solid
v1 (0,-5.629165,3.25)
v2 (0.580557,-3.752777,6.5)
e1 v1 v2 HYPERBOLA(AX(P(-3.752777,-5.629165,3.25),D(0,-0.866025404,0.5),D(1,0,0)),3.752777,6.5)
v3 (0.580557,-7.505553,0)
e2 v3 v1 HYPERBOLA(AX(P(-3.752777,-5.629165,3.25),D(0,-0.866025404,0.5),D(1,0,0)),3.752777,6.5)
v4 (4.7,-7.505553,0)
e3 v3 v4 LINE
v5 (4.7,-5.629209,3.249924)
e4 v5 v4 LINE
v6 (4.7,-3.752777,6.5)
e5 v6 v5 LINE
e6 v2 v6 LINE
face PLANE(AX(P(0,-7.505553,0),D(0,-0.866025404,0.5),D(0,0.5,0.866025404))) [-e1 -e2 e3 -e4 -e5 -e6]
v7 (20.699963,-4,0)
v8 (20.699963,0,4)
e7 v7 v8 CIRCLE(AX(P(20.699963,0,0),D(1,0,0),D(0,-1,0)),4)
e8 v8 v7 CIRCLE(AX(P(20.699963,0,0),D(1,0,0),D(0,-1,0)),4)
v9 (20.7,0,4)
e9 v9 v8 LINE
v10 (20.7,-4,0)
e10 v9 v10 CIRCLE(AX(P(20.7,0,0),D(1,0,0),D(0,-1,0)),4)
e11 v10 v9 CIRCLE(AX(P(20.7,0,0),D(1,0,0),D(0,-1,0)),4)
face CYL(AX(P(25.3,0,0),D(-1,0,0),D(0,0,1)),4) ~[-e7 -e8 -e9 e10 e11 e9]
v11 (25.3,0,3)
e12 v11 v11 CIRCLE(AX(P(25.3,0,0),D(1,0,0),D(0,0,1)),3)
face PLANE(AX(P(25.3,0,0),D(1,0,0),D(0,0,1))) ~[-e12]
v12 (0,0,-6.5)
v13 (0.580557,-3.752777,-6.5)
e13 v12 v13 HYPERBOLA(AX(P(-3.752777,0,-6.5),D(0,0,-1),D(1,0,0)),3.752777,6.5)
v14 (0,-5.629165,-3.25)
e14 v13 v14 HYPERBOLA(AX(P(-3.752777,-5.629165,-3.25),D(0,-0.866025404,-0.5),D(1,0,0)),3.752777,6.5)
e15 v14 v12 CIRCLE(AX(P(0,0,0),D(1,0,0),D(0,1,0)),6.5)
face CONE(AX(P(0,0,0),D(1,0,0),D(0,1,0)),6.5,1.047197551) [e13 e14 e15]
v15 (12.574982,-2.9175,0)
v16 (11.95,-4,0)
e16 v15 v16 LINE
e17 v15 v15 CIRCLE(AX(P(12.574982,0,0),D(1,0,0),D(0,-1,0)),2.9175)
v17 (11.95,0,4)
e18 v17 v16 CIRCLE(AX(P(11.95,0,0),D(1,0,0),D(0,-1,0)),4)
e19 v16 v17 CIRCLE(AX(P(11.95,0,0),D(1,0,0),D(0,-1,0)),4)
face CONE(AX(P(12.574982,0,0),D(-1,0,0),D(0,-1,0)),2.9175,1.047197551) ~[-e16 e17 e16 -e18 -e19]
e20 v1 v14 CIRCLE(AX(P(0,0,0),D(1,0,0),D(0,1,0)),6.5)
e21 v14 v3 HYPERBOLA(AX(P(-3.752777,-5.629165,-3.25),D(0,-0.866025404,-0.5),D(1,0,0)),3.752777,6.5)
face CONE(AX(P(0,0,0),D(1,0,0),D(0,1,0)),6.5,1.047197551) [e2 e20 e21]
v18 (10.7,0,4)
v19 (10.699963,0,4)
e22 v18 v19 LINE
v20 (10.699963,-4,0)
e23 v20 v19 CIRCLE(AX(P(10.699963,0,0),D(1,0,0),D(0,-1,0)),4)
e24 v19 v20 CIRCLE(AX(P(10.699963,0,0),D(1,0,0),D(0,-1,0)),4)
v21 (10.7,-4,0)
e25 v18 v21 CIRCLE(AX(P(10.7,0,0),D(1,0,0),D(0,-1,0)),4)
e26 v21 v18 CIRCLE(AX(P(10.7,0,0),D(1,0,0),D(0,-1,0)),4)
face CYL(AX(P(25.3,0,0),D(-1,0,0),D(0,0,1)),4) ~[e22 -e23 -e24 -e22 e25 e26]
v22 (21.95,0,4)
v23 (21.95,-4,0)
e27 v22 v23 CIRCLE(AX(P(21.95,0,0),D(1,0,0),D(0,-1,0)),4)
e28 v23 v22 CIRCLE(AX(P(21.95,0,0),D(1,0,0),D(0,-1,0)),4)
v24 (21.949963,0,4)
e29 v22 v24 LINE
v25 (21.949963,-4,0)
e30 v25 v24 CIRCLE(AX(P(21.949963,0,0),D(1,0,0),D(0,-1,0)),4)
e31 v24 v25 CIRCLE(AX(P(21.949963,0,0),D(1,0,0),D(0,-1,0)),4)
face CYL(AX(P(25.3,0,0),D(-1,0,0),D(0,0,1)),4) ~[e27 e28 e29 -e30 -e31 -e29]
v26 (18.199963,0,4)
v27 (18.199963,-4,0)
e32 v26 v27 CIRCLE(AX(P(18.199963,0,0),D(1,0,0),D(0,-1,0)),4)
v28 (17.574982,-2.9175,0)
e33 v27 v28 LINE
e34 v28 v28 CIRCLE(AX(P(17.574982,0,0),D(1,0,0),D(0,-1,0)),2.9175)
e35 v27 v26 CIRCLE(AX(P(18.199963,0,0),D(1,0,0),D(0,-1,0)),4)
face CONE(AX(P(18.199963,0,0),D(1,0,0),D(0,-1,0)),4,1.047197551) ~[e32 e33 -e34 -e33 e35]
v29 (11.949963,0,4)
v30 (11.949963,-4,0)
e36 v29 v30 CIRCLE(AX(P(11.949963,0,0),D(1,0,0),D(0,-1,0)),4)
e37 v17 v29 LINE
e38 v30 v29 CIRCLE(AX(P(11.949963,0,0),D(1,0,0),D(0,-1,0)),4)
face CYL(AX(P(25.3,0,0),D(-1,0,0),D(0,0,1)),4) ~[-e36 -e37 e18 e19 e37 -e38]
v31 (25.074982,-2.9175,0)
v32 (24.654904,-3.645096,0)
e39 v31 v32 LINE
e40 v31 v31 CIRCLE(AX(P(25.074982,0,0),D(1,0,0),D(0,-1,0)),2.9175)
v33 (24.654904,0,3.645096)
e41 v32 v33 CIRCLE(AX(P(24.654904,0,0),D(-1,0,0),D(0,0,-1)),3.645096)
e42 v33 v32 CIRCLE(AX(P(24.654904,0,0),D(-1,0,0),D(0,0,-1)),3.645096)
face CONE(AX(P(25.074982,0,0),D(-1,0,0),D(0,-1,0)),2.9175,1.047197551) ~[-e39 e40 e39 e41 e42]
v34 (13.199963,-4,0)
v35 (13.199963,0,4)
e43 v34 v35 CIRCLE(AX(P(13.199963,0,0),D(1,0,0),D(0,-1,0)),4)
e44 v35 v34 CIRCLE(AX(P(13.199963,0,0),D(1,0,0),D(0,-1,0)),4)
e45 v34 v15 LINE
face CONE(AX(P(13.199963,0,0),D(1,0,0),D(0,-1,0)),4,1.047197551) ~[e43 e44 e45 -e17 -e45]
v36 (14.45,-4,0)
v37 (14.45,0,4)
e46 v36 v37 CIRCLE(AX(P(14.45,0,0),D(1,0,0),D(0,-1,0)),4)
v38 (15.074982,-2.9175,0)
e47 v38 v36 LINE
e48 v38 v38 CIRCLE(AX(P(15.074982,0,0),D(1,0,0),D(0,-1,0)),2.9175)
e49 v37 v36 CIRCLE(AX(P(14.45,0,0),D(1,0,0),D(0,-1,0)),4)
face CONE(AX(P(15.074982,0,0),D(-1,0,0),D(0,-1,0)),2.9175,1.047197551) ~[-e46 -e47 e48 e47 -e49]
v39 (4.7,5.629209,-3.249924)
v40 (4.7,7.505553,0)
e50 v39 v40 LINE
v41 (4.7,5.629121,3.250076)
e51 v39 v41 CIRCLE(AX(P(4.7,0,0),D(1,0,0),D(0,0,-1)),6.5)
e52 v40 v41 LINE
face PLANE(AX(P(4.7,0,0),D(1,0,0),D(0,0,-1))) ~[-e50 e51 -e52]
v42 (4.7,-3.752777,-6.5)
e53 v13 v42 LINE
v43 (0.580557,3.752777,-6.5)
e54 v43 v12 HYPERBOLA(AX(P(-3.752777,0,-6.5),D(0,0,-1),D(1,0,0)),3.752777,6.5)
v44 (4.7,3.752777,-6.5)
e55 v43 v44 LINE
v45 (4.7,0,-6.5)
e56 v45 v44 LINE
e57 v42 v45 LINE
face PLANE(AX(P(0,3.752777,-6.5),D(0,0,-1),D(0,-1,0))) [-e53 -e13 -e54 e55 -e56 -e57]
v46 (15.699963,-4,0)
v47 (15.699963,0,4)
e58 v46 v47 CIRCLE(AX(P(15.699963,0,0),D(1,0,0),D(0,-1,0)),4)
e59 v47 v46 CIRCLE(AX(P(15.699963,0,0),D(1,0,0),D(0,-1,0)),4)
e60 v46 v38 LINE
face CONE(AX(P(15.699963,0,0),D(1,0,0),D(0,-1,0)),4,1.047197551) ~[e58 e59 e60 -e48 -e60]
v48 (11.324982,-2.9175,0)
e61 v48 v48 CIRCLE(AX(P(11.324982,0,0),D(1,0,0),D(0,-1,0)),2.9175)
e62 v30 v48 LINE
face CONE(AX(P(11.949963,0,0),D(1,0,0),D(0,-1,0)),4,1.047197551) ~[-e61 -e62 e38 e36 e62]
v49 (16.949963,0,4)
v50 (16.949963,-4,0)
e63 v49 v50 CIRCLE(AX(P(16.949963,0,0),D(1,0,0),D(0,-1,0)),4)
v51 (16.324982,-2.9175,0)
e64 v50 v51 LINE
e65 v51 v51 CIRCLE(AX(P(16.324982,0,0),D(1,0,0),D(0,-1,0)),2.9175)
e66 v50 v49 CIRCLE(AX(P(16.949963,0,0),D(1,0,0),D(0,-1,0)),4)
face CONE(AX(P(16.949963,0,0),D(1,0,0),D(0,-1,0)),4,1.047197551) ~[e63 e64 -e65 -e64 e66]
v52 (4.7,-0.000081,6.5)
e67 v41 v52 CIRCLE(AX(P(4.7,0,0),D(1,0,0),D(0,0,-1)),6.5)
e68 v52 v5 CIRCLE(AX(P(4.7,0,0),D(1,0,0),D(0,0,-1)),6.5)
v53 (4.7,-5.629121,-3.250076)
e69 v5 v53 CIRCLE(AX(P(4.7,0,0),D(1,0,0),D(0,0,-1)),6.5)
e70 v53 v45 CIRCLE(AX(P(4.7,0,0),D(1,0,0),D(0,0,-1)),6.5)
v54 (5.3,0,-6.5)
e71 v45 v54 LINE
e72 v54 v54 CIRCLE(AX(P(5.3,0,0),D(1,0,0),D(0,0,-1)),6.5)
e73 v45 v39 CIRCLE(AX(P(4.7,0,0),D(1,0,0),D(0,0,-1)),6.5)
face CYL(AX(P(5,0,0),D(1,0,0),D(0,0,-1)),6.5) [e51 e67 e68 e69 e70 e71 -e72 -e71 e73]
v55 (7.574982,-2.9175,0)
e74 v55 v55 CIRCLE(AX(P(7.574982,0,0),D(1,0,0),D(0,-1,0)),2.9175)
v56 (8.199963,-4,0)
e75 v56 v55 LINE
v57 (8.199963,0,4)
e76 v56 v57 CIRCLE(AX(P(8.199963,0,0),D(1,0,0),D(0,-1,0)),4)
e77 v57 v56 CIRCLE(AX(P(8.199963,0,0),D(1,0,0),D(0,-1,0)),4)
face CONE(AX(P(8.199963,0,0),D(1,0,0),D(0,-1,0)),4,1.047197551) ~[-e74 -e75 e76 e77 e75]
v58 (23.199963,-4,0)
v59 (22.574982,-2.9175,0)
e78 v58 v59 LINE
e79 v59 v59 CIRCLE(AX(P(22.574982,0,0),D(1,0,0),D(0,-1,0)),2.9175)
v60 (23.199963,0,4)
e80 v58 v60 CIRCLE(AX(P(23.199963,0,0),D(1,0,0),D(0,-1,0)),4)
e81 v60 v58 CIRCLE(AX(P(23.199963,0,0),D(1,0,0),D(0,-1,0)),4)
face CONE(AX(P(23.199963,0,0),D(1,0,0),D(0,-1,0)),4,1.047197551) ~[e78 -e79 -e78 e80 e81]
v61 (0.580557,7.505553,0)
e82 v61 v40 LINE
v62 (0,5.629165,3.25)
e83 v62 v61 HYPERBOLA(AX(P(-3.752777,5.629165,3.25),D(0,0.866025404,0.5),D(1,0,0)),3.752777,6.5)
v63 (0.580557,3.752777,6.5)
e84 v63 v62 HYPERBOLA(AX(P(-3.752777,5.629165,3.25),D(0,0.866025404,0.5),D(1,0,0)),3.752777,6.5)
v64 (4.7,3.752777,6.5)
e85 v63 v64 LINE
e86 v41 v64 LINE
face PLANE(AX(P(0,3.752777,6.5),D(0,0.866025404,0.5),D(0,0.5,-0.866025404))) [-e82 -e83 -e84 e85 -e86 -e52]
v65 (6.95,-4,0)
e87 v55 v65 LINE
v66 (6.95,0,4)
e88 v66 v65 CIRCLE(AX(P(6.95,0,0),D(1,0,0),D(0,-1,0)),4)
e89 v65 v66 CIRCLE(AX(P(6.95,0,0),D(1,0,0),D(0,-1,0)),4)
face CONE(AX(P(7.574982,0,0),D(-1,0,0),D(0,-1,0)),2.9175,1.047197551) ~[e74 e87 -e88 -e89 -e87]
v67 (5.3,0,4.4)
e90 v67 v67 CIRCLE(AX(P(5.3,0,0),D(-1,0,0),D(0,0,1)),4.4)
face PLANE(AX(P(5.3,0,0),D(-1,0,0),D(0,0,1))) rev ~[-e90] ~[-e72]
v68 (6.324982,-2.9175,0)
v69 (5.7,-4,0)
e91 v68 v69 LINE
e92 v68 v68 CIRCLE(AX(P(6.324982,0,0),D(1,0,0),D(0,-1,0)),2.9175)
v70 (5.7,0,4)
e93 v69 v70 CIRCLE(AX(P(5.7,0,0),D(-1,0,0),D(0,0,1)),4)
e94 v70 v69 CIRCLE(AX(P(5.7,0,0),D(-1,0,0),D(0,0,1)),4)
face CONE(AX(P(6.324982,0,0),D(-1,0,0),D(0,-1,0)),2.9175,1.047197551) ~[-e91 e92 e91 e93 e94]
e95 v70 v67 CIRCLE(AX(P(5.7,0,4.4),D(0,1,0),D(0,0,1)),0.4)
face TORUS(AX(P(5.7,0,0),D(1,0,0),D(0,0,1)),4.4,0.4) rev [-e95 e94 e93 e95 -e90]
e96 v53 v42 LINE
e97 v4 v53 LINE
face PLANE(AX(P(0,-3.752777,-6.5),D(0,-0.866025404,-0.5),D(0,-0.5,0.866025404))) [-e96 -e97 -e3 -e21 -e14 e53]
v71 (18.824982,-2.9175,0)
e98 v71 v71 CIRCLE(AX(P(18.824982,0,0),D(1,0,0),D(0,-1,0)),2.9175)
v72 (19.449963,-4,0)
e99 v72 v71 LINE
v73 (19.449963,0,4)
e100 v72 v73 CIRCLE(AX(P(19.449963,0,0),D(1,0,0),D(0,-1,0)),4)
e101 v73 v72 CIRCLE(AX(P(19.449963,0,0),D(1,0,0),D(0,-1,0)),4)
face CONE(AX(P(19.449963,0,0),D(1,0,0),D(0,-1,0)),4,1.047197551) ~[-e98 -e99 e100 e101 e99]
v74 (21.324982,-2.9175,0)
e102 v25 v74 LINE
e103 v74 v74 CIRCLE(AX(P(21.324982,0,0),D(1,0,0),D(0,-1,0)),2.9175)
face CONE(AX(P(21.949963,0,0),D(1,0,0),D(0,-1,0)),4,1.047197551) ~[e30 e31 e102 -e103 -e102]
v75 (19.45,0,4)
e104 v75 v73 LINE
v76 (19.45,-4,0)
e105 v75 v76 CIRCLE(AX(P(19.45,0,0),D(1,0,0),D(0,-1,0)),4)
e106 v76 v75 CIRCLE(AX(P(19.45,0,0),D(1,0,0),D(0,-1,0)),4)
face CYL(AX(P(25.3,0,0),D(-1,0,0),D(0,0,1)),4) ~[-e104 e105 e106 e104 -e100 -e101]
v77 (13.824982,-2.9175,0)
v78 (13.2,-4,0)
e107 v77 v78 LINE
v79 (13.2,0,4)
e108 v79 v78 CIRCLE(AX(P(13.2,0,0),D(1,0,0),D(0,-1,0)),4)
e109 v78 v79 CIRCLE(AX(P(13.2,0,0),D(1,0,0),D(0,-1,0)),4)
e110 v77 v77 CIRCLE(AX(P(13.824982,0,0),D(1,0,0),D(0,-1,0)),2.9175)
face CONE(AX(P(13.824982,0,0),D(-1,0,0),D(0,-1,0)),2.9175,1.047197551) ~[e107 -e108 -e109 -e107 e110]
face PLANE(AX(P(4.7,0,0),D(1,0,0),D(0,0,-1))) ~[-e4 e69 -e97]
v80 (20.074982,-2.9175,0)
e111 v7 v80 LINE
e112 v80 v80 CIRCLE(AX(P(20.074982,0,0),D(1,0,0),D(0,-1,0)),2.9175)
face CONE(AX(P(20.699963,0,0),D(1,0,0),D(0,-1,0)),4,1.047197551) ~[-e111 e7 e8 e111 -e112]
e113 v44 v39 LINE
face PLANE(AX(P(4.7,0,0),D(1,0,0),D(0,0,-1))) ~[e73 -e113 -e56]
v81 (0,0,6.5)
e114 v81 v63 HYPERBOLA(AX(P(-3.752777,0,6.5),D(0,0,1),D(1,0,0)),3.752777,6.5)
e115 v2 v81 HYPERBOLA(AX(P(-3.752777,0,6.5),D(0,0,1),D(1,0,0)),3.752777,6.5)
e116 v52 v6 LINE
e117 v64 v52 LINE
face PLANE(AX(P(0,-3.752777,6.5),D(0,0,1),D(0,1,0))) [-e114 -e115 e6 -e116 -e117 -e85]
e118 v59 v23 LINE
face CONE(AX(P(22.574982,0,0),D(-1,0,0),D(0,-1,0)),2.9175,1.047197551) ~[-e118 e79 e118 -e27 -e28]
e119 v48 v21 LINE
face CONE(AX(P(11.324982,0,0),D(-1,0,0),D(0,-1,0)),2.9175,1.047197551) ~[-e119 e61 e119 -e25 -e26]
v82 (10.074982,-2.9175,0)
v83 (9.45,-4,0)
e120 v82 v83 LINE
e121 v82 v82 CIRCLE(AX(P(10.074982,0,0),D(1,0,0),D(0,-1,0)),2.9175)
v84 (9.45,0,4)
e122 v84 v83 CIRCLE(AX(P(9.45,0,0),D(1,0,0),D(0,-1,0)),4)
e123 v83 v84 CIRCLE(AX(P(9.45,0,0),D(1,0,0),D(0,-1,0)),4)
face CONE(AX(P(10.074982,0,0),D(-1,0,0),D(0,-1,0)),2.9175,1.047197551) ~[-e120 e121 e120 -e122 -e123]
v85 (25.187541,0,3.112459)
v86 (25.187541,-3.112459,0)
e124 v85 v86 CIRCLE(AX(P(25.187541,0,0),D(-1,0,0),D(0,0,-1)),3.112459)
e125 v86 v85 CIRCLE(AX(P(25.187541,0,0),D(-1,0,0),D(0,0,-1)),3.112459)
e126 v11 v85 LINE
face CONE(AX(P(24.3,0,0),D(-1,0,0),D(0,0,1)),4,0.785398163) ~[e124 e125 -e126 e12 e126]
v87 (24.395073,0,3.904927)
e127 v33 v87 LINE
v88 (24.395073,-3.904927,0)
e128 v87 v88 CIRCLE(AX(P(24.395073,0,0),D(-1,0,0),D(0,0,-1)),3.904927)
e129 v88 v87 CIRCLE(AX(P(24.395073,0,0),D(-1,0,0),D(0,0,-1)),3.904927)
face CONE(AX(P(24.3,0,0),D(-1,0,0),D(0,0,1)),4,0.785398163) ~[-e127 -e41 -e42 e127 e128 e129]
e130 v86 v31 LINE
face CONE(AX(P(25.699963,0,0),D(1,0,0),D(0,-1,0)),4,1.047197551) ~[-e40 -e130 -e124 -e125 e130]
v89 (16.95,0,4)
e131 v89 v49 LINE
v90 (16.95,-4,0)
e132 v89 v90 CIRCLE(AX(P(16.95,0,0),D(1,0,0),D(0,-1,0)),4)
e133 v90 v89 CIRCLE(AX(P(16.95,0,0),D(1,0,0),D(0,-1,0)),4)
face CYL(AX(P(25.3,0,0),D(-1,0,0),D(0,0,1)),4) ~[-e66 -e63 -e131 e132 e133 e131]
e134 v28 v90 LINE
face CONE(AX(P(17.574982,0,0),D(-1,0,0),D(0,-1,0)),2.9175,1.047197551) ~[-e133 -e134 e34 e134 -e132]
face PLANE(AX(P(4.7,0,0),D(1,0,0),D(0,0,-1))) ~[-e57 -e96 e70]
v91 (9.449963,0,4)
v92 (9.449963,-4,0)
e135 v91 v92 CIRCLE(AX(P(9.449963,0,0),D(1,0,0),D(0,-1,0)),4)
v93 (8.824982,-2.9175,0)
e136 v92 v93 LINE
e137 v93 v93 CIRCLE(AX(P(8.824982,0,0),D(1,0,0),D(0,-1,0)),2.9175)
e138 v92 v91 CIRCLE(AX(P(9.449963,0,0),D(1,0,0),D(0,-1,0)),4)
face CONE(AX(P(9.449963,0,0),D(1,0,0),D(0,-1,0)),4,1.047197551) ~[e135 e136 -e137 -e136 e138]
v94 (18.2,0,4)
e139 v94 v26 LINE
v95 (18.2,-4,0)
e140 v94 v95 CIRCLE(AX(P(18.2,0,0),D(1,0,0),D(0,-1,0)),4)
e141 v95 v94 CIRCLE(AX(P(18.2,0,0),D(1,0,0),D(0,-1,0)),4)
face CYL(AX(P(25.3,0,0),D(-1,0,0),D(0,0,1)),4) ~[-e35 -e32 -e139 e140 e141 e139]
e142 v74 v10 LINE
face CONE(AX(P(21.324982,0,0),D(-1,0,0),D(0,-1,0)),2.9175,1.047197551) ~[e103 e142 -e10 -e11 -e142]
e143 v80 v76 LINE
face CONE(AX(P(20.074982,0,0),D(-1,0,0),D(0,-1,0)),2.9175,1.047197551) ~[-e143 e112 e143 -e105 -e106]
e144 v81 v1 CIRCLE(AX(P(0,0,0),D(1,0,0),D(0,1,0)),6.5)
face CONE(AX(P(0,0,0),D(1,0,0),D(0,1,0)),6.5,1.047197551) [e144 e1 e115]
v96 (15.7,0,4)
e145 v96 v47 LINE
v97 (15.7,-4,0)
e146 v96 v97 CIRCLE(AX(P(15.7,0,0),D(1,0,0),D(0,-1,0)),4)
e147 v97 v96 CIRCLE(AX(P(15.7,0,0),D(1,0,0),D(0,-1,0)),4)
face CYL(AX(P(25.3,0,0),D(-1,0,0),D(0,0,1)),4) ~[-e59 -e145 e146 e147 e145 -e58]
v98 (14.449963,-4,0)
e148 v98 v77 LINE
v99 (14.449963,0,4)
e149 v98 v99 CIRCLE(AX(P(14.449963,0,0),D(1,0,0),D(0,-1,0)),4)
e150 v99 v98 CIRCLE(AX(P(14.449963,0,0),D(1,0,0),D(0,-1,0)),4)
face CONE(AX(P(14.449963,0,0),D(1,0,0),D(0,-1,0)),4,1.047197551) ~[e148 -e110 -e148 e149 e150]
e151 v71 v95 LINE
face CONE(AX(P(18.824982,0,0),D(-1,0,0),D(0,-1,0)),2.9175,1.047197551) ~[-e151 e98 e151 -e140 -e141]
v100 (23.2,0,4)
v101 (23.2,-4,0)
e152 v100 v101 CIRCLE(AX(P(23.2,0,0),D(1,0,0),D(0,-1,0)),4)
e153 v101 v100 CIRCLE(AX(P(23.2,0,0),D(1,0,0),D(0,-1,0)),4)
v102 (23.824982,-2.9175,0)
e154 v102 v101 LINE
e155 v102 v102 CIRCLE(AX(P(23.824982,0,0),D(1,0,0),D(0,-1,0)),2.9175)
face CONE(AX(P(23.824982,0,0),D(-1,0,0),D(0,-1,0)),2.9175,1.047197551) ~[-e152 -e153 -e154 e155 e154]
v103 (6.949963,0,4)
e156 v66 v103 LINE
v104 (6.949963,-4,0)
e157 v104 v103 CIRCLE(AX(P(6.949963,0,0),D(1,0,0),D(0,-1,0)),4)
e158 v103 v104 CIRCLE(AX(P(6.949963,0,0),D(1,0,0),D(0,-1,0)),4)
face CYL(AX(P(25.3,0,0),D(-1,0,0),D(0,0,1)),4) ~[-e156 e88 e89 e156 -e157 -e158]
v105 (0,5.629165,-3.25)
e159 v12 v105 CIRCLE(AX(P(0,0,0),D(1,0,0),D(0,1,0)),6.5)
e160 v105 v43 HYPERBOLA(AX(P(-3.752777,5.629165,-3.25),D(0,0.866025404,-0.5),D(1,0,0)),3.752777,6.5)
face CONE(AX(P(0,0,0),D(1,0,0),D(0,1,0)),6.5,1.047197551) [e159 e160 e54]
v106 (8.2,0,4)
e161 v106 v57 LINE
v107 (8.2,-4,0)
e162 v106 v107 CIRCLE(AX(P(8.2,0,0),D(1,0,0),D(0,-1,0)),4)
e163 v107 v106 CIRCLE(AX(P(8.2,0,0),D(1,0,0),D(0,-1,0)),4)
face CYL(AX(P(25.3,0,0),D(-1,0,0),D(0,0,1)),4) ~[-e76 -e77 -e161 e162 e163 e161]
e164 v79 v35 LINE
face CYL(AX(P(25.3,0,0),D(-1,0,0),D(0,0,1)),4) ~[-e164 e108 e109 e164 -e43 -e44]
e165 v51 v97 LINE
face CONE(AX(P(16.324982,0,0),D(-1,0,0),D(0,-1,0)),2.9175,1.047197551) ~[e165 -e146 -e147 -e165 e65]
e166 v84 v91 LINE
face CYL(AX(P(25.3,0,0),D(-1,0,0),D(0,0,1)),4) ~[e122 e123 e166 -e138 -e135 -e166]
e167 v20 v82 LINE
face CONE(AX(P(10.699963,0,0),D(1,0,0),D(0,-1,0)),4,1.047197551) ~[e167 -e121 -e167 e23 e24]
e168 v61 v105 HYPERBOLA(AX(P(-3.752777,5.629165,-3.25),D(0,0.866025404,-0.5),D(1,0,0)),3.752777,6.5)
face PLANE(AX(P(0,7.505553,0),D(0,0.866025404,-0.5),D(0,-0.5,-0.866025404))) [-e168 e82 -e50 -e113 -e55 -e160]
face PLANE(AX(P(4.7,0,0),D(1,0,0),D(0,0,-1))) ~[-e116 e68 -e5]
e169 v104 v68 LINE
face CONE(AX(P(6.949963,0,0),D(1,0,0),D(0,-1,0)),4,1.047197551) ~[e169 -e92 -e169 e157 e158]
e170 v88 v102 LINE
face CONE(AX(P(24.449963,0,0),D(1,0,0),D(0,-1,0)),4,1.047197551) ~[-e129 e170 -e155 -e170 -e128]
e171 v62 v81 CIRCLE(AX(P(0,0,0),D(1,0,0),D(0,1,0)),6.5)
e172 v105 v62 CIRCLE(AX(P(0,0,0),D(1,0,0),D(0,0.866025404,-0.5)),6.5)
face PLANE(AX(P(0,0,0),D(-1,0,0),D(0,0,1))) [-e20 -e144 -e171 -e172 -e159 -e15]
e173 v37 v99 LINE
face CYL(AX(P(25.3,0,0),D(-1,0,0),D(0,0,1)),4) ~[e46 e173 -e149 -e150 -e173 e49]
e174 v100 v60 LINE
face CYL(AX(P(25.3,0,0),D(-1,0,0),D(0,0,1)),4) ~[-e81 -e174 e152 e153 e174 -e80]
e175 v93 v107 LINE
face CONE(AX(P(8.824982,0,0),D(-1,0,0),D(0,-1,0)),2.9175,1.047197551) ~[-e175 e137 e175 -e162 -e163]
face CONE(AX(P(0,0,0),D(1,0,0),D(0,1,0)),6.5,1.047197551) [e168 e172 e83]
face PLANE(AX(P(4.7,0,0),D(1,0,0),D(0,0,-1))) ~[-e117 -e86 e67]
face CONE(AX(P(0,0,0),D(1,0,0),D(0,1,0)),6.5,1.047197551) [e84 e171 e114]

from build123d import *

# Parameters (mm, degrees)
EXTRUDE_374_DEPTH      = 5.3
SKETCH_4_W             = 0.6
SKETCH_4_H             = 11.005553499
CHAMFER_1917_SIZE      = 1
FILLET_1962_R          = 0.4
PATTERN_LINEAR_1_COUNT = 16
PATTERN_LINEAR_1_PITCH = 1.25


with BuildPart() as part:
    # 草图1 → Extrude 374 (new body)
    with BuildSketch(Plane(origin=(0, 0, 0), x_dir=(0, 0, -1), z_dir=(1, 0, 0))):
        Polygon((6.5, 3.75277675), (6.5, -3.75277675), (0, -7.505553499), (-6.5, -3.75277675), (-6.5, 3.75277675), (0, 7.505553499), align=None)
    extrude(amount=EXTRUDE_374_DEPTH)

    # 草图2 → 凸台-旋转1 (revolve)
    with BuildSketch(Plane.XY, mode=Mode.PRIVATE) as revolve_1_sk:
        Polygon((0, 0), (25.3, 0), (25.3, 2.9175), (25.3, 4), (0, 4), align=None)
    revolve(revolve_1_sk.sketch.rotate(Axis((0, 0, 0), (1, 0, 0)), 90), axis=Axis((0, 0, 0), (1, 0, 0)))

    # 草图3 → 切除-旋转1 (revolve, cut)
    with BuildSketch(Plane.XY):
        Polygon((0, 6.5), (3.46730793, 12.505553499), (3.46730793, 17.505553499), (-10, 17.505553499), (-10, 6.5), align=None)
    revolve(axis=Axis((0, 0, 0), (1, 0, 0)), mode=Mode.SUBTRACT)

    # 草图5 → 切除-旋转2 (revolve, cut)
    with BuildSketch(Plane.XY):
        Polygon((5.3, 6.5), (1.83269207, 12.505553499), (1.83269207, 17.505553499), (11.83269207, 17.505553499), (11.83269207, 6.5), align=None)
    revolve(axis=Axis((0, 0, 0), (1, 0, 0)), mode=Mode.SUBTRACT)

    # 草图4 → 切除-旋转3 (revolve, cut)
    with BuildSketch(Plane.XY, mode=Mode.PRIVATE) as cut_revolve_3_sk:
        with Locations((5, 12.00277675)):
            Rectangle(SKETCH_4_W, SKETCH_4_H)
    revolve(cut_revolve_3_sk.sketch.rotate(Axis((0, 0, 0), (1, 0, 0)), 270), axis=Axis((0, 0, 0), (1, 0, 0)), mode=Mode.SUBTRACT)

    # Chamfer 1917
    chamfer_1917_edges = [part.edges().sort_by_distance(p)[0] for p in [
        (25.3, 0, -4),
    ]]
    chamfer(chamfer_1917_edges, length=CHAMFER_1917_SIZE)

    # Fillet 1962
    fillet_1962_edges = [part.edges().sort_by_distance(p)[0] for p in [
        (5.3, 0, -4),
    ]]
    fillet(fillet_1962_edges, radius=FILLET_1962_R)

    # 草图6 → 切除-旋转4 (revolve, cut)
    with BuildSketch(Plane.XY):
        Polygon((6.324981666, -2.9175), (5.7, -4), (5.7, -5), (6.949963333, -5), (6.949963333, -4), align=None)
    cut_revolve_4 = revolve(axis=Axis((-3.175, 0, 0), (1, 0, 0)), mode=Mode.SUBTRACT)

    # 阵列(线性)1: 切除-旋转4 ×16
    with Locations(*[(i * PATTERN_LINEAR_1_PITCH, 0, 0) for i in range(1, PATTERN_LINEAR_1_COUNT)]):
        add(cut_revolve_4, mode=Mode.SUBTRACT)


solid = part.part
